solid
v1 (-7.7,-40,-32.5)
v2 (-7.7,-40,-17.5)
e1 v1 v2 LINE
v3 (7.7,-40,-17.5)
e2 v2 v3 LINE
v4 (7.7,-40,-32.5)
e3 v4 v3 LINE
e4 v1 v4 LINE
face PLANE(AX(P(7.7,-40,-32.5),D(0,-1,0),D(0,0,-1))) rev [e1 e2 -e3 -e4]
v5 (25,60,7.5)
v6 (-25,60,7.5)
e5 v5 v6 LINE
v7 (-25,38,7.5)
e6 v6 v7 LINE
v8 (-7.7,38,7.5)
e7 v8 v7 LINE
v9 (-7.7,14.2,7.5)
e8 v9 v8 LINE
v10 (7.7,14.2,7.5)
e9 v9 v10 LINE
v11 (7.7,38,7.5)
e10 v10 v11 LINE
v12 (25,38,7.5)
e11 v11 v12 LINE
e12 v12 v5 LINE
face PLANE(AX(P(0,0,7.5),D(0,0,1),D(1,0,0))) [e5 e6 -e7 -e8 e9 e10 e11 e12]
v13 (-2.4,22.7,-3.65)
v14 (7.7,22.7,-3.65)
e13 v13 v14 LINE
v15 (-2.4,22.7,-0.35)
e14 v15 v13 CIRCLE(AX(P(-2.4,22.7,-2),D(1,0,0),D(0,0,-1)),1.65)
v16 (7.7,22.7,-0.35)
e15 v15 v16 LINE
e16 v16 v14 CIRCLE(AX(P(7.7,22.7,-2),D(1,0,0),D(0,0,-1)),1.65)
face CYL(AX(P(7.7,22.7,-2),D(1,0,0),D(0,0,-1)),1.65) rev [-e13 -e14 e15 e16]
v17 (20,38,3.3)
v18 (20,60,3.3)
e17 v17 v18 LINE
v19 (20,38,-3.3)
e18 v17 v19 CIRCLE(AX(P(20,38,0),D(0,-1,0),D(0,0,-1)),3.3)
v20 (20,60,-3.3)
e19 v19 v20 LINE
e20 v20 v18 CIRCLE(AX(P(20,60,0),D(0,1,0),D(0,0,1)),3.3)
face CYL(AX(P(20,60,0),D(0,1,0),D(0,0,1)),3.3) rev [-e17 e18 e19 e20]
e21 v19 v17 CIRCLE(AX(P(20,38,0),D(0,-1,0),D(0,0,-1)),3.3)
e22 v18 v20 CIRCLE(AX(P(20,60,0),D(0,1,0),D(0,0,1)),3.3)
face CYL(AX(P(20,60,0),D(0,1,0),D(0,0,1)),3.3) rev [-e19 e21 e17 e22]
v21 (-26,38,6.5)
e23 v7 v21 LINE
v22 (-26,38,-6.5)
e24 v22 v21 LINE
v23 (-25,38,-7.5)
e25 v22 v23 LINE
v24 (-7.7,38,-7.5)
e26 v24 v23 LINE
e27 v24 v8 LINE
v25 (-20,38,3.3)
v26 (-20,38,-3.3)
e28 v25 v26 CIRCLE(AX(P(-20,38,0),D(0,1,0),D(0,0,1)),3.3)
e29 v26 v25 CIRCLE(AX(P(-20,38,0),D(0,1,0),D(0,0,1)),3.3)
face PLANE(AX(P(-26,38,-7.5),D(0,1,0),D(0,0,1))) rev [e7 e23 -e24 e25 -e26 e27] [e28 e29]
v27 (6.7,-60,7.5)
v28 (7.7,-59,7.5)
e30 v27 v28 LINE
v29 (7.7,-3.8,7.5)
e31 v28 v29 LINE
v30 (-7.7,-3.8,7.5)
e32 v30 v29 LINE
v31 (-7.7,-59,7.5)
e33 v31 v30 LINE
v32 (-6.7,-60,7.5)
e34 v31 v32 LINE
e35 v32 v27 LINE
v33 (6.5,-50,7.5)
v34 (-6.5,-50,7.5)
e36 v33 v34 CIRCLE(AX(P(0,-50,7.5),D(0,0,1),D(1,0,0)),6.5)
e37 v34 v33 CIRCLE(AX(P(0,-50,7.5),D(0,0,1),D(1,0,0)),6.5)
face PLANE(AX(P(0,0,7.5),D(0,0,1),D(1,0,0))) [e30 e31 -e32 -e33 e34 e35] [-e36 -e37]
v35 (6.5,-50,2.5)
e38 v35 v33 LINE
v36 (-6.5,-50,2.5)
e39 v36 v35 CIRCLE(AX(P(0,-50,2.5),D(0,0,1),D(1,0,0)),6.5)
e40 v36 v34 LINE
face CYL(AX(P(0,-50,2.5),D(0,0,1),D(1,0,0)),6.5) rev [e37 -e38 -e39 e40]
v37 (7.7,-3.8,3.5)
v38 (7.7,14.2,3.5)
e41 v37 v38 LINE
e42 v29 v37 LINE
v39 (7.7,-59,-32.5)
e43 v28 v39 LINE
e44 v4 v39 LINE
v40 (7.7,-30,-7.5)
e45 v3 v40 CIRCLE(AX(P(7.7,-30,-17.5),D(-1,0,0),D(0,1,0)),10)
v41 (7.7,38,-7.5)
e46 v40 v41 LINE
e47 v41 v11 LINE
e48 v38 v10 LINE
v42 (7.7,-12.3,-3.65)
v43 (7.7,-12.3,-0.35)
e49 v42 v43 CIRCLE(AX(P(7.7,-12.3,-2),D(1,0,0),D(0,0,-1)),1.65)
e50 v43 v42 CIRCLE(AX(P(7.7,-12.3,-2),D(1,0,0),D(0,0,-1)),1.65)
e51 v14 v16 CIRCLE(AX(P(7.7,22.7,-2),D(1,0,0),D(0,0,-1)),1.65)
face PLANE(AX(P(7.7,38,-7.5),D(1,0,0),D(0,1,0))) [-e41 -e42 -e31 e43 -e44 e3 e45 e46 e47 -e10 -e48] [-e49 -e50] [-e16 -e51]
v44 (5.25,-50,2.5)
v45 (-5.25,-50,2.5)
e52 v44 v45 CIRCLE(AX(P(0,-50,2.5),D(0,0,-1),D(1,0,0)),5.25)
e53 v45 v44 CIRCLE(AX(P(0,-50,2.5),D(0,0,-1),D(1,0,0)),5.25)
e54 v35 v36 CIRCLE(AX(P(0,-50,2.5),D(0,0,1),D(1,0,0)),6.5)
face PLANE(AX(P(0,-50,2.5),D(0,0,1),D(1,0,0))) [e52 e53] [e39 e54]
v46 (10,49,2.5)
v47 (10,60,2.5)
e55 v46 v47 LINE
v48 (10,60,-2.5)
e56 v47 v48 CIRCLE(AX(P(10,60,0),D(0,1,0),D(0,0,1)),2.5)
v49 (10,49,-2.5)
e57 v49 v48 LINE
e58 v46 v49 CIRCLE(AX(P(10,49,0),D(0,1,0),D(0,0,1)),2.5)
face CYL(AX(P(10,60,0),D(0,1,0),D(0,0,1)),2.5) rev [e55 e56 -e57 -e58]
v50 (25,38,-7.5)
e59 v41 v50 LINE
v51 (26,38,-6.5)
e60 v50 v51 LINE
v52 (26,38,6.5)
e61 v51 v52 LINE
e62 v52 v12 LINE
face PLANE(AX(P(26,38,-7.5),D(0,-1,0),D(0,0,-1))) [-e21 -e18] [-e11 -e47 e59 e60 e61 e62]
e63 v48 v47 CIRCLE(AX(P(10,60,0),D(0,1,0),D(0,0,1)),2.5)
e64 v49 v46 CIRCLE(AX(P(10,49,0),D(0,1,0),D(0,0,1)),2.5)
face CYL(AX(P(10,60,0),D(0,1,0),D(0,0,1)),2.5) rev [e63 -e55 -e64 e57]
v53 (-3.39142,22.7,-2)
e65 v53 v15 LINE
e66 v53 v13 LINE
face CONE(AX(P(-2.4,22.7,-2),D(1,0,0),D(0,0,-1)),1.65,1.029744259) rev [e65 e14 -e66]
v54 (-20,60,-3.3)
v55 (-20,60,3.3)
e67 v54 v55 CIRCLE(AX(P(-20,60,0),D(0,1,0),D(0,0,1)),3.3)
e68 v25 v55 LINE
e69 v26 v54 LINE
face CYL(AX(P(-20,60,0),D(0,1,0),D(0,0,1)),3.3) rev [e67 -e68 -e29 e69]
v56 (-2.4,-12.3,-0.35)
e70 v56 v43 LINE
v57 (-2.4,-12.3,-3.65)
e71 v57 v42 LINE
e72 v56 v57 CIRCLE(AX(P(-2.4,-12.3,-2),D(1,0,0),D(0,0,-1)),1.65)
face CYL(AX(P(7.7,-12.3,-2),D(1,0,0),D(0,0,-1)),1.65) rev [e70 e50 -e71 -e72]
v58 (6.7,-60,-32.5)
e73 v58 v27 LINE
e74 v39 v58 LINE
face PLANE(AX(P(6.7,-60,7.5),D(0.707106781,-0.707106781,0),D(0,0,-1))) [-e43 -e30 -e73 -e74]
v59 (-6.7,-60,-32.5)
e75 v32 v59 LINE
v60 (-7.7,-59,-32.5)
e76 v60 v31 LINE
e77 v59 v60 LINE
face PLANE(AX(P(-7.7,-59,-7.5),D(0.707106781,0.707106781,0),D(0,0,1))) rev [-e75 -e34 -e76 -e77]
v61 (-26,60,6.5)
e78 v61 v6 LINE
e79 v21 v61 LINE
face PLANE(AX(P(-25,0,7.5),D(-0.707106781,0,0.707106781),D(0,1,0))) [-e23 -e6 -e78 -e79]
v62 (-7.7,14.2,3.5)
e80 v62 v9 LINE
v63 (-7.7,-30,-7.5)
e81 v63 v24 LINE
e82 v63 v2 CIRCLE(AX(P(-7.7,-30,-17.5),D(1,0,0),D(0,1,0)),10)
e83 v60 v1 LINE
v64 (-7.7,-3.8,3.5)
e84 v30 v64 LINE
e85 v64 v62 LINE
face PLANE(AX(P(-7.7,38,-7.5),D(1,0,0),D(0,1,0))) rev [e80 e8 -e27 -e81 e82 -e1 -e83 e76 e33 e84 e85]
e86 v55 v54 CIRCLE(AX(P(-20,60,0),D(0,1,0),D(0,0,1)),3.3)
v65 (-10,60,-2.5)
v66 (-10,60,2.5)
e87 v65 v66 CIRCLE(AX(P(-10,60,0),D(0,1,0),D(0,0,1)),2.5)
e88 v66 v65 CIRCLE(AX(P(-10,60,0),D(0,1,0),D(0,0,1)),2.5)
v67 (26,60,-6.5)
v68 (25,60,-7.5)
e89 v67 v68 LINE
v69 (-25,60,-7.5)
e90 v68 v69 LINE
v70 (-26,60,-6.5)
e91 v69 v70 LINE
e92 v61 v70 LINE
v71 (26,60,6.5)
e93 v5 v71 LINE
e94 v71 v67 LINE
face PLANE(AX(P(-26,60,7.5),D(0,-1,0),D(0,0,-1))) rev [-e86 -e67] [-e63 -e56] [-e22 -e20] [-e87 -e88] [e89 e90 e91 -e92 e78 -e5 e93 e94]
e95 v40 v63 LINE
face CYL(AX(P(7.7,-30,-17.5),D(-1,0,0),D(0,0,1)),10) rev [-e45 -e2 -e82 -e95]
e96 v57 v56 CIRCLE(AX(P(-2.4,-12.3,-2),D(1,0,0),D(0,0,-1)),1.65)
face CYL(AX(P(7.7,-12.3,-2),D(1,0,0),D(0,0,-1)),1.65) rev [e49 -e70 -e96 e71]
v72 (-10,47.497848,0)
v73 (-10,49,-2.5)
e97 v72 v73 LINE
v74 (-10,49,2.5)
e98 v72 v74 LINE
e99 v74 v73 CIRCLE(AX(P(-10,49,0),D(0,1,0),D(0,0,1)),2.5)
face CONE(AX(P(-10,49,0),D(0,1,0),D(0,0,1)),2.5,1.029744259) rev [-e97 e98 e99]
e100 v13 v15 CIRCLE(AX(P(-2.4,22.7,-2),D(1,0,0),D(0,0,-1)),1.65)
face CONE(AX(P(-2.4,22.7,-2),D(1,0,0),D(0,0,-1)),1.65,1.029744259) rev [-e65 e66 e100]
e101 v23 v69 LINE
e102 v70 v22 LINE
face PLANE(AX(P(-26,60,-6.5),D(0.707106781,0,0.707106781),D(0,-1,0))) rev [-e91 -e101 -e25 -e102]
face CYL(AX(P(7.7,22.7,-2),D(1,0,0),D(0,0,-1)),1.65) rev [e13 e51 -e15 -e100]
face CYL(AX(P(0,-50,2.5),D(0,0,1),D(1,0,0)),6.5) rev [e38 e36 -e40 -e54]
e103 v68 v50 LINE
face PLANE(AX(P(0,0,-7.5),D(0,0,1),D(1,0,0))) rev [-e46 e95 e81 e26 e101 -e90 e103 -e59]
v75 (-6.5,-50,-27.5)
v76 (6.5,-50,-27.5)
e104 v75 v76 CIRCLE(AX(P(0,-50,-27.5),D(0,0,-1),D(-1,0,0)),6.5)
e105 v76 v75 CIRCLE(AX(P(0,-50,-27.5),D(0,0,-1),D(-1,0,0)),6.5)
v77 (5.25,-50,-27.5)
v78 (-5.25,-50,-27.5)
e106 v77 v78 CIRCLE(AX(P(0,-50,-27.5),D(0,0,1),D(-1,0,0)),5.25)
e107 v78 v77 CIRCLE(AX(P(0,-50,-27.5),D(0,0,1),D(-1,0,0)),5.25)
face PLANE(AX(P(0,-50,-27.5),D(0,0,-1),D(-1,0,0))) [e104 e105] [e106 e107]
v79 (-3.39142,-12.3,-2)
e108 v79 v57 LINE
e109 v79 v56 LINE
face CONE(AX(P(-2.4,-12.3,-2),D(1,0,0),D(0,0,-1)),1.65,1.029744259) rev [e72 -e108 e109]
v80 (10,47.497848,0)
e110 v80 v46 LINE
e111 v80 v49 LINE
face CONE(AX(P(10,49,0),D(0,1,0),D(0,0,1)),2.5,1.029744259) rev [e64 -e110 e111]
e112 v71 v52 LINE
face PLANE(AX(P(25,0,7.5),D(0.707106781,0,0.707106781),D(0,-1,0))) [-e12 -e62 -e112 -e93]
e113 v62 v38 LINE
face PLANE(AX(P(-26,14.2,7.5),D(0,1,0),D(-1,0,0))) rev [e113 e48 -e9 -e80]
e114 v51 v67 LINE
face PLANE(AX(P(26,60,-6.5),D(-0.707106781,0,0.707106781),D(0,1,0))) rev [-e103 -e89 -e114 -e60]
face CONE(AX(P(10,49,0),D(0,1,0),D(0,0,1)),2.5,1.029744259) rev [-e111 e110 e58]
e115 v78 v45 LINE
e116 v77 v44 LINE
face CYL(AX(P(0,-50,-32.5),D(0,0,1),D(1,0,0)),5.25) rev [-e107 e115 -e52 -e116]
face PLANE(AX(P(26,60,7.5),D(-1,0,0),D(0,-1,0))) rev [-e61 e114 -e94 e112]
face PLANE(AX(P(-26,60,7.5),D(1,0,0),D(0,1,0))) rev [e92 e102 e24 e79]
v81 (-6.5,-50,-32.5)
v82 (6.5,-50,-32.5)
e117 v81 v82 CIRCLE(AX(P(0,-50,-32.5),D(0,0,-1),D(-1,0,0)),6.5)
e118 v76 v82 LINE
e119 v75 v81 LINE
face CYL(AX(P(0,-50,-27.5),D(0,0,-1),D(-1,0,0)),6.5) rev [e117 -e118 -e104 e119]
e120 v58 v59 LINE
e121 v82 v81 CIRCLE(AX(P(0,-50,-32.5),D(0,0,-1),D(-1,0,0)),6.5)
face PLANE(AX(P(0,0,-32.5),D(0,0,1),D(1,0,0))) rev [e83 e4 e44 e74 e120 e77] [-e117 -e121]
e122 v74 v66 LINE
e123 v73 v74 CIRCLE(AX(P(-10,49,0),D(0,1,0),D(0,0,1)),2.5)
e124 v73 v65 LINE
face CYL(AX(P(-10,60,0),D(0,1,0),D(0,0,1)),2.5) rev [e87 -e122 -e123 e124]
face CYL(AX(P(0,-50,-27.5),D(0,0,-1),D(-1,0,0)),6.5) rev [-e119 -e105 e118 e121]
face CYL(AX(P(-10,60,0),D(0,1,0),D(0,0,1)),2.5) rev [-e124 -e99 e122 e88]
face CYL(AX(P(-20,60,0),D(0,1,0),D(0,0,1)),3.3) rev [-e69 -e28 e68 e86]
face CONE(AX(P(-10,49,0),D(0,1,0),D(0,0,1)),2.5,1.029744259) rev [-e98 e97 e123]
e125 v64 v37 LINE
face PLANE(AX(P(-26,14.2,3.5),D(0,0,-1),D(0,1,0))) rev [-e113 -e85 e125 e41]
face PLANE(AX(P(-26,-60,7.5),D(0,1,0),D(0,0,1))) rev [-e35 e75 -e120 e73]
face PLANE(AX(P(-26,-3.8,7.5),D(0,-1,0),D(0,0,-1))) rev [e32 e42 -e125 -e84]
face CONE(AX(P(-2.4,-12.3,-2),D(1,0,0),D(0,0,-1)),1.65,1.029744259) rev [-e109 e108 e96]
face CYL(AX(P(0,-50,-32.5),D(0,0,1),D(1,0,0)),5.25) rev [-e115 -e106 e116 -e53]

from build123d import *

# Parameters (mm, degrees)
SKETCH1_W                     = 52
SKETCH1_H                     = 120
BOSS_EXTRUDE1_DEPTH           = 7.5
SKETCH8_W                     = 18.3
SKETCH8_H                     = 98
CUT_EXTRUDE4_DEPTH            = 68.089492471
F_6_6_6_6_DIAMETER_HOLE1_D    = 6.6
CHAMFER1_SIZE                 = 1
BLIND_PIN_HOLE1_SIZE_MM_D     = 5
BLIND_PIN_HOLE1_SIZE_MM_DEPTH = 11
BLIND_PIN_HOLE1_SIZE_MM_TIP   = 1.502151548
BOSS_EXTRUDE2_DEPTH           = 25
FILLET1_R                     = 10
SKETCH14_R                    = 5.25
CUT_EXTRUDE5_DEPTH            = 77.655071587
SKETCH15_R                    = 6.5
CUT_EXTRUDE6_DEPTH            = 5
CUT_EXTRUDE7_START            = -5
SKETCH16_R                    = 6.5
CUT_EXTRUDE7_DEPTH            = 5
SKETCH17_W                    = 4
SKETCH17_H                    = 18
CUT_EXTRUDE8_DEPTH            = 77.104796169
M4_TAPPED_HOLE1_D             = 3.3
M4_TAPPED_HOLE1_DEPTH         = 10.1
M4_TAPPED_HOLE1_TIP           = 0.991420021


with BuildPart() as part:
    # Sketch1 → Boss-Extrude1 (new, symmetric)
    with BuildSketch(Plane.XY):
        Rectangle(SKETCH1_W, SKETCH1_H)
    extrude(amount=BOSS_EXTRUDE1_DEPTH, both=True)

    # Sketch8 → Cut-Extrude4 (cut, through all)
    with BuildSketch(Plane.XY.offset(7.5)):
        with Locations((-16.85, -11)):
            Rectangle(SKETCH8_W, SKETCH8_H)
    cut_extrude4 = extrude(amount=-CUT_EXTRUDE4_DEPTH, mode=Mode.SUBTRACT)

    # Mirror1: Cut-Extrude4 across plane
    add(cut_extrude4.mirror(Plane(origin=(0, 0, 0), x_dir=(0, 0, 1), z_dir=(1, 0, 0))), mode=Mode.SUBTRACT)

    # Ø6.6 (6.6) Diameter Hole1 (through all)
    with Locations(Plane(origin=(0, 60, 0), x_dir=(1, 0, 0), z_dir=(0, 1, 0))):
        with Locations((-20, 0), (20, 0)):
            Hole(F_6_6_6_6_DIAMETER_HOLE1_D / 2)

    # Chamfer1
    chamfer1_edges = [part.edges().sort_by_distance(p)[0] for p in [
        (-26, 49, 7.5),
        (-7.7, -60, 0),
        (26, 49, -7.5),
        (26, 49, 7.5),
        (7.7, -60, 0),
        (-26, 49, -7.5),
    ]]
    chamfer(chamfer1_edges, length=CHAMFER1_SIZE)

    # Blind Pin Hole1 size mm
    with Locations(Plane(origin=(0, 60, 0), x_dir=(1, 0, 0), z_dir=(0, 1, 0))):
        with Locations((-10, 0), (10, 0)):
            Hole(BLIND_PIN_HOLE1_SIZE_MM_D / 2, depth=BLIND_PIN_HOLE1_SIZE_MM_DEPTH)
            with Locations((0, 0, -(BLIND_PIN_HOLE1_SIZE_MM_DEPTH + BLIND_PIN_HOLE1_SIZE_MM_TIP / 2))):  # 118° drill point
                Cone(0, BLIND_PIN_HOLE1_SIZE_MM_D / 2, BLIND_PIN_HOLE1_SIZE_MM_TIP, mode=Mode.SUBTRACT)

    # Sketch13 → Boss-Extrude2 (add)
    with BuildSketch(Plane(origin=(0, 0, -7.5), x_dir=(-1, 0, 0), z_dir=(0, 0, -1))):
        Polygon((-7.7, -40), (7.7, -40), (7.7, -59), (6.7, -60), (-6.7, -60), (-7.7, -59), align=None)
    extrude(amount=BOSS_EXTRUDE2_DEPTH)

    # Fillet1
    fillet1_edges = [part.edges().sort_by_distance(p)[0] for p in [
        (0, -40, -7.5),
    ]]
    fillet(fillet1_edges, radius=FILLET1_R)

    # Sketch14 → Cut-Extrude5 (cut, through all)
    with BuildSketch(Plane.XY.offset(7.5)):
        with Locations((0, -50)):
            Circle(SKETCH14_R)
    extrude(amount=-CUT_EXTRUDE5_DEPTH, mode=Mode.SUBTRACT)

    # Sketch15 → Cut-Extrude6 (cut)
    with BuildSketch(Plane.XY.offset(7.5)):
        with Locations((0, -50)):
            Circle(SKETCH15_R)
    extrude(amount=-CUT_EXTRUDE6_DEPTH, mode=Mode.SUBTRACT)

    # Sketch16 → Cut-Extrude7 (cut)
    with BuildSketch(Plane(origin=(0, 0, -32.5), x_dir=(-1, 0, 0), z_dir=(0, 0, -1)).offset(CUT_EXTRUDE7_START)):
        with Locations(Location((0, -50, 0), (0, 0, 180))):
            Circle(SKETCH16_R)
    extrude(amount=CUT_EXTRUDE7_DEPTH, mode=Mode.SUBTRACT)

    # Sketch17 → Cut-Extrude8 (cut, through all)
    with BuildSketch(Plane(origin=(7.7, 0, 0), x_dir=(0, 0, -1), z_dir=(1, 0, 0))):
        with Locations((-5.5, 5.2)):
            Rectangle(SKETCH17_W, SKETCH17_H)
    extrude(amount=-CUT_EXTRUDE8_DEPTH, mode=Mode.SUBTRACT)

    # M4 Tapped Hole1
    with Locations(Plane(origin=(7.7, 0, 0), x_dir=(0, 0, -1), z_dir=(1, 0, 0))):
        with Locations((2, 22.7), (2, -12.3)):
            Hole(M4_TAPPED_HOLE1_D / 2, depth=M4_TAPPED_HOLE1_DEPTH)
            with Locations((0, 0, -(M4_TAPPED_HOLE1_DEPTH + M4_TAPPED_HOLE1_TIP / 2))):  # 118° drill point
                Cone(0, M4_TAPPED_HOLE1_D / 2, M4_TAPPED_HOLE1_TIP, mode=Mode.SUBTRACT)


solid = part.part
